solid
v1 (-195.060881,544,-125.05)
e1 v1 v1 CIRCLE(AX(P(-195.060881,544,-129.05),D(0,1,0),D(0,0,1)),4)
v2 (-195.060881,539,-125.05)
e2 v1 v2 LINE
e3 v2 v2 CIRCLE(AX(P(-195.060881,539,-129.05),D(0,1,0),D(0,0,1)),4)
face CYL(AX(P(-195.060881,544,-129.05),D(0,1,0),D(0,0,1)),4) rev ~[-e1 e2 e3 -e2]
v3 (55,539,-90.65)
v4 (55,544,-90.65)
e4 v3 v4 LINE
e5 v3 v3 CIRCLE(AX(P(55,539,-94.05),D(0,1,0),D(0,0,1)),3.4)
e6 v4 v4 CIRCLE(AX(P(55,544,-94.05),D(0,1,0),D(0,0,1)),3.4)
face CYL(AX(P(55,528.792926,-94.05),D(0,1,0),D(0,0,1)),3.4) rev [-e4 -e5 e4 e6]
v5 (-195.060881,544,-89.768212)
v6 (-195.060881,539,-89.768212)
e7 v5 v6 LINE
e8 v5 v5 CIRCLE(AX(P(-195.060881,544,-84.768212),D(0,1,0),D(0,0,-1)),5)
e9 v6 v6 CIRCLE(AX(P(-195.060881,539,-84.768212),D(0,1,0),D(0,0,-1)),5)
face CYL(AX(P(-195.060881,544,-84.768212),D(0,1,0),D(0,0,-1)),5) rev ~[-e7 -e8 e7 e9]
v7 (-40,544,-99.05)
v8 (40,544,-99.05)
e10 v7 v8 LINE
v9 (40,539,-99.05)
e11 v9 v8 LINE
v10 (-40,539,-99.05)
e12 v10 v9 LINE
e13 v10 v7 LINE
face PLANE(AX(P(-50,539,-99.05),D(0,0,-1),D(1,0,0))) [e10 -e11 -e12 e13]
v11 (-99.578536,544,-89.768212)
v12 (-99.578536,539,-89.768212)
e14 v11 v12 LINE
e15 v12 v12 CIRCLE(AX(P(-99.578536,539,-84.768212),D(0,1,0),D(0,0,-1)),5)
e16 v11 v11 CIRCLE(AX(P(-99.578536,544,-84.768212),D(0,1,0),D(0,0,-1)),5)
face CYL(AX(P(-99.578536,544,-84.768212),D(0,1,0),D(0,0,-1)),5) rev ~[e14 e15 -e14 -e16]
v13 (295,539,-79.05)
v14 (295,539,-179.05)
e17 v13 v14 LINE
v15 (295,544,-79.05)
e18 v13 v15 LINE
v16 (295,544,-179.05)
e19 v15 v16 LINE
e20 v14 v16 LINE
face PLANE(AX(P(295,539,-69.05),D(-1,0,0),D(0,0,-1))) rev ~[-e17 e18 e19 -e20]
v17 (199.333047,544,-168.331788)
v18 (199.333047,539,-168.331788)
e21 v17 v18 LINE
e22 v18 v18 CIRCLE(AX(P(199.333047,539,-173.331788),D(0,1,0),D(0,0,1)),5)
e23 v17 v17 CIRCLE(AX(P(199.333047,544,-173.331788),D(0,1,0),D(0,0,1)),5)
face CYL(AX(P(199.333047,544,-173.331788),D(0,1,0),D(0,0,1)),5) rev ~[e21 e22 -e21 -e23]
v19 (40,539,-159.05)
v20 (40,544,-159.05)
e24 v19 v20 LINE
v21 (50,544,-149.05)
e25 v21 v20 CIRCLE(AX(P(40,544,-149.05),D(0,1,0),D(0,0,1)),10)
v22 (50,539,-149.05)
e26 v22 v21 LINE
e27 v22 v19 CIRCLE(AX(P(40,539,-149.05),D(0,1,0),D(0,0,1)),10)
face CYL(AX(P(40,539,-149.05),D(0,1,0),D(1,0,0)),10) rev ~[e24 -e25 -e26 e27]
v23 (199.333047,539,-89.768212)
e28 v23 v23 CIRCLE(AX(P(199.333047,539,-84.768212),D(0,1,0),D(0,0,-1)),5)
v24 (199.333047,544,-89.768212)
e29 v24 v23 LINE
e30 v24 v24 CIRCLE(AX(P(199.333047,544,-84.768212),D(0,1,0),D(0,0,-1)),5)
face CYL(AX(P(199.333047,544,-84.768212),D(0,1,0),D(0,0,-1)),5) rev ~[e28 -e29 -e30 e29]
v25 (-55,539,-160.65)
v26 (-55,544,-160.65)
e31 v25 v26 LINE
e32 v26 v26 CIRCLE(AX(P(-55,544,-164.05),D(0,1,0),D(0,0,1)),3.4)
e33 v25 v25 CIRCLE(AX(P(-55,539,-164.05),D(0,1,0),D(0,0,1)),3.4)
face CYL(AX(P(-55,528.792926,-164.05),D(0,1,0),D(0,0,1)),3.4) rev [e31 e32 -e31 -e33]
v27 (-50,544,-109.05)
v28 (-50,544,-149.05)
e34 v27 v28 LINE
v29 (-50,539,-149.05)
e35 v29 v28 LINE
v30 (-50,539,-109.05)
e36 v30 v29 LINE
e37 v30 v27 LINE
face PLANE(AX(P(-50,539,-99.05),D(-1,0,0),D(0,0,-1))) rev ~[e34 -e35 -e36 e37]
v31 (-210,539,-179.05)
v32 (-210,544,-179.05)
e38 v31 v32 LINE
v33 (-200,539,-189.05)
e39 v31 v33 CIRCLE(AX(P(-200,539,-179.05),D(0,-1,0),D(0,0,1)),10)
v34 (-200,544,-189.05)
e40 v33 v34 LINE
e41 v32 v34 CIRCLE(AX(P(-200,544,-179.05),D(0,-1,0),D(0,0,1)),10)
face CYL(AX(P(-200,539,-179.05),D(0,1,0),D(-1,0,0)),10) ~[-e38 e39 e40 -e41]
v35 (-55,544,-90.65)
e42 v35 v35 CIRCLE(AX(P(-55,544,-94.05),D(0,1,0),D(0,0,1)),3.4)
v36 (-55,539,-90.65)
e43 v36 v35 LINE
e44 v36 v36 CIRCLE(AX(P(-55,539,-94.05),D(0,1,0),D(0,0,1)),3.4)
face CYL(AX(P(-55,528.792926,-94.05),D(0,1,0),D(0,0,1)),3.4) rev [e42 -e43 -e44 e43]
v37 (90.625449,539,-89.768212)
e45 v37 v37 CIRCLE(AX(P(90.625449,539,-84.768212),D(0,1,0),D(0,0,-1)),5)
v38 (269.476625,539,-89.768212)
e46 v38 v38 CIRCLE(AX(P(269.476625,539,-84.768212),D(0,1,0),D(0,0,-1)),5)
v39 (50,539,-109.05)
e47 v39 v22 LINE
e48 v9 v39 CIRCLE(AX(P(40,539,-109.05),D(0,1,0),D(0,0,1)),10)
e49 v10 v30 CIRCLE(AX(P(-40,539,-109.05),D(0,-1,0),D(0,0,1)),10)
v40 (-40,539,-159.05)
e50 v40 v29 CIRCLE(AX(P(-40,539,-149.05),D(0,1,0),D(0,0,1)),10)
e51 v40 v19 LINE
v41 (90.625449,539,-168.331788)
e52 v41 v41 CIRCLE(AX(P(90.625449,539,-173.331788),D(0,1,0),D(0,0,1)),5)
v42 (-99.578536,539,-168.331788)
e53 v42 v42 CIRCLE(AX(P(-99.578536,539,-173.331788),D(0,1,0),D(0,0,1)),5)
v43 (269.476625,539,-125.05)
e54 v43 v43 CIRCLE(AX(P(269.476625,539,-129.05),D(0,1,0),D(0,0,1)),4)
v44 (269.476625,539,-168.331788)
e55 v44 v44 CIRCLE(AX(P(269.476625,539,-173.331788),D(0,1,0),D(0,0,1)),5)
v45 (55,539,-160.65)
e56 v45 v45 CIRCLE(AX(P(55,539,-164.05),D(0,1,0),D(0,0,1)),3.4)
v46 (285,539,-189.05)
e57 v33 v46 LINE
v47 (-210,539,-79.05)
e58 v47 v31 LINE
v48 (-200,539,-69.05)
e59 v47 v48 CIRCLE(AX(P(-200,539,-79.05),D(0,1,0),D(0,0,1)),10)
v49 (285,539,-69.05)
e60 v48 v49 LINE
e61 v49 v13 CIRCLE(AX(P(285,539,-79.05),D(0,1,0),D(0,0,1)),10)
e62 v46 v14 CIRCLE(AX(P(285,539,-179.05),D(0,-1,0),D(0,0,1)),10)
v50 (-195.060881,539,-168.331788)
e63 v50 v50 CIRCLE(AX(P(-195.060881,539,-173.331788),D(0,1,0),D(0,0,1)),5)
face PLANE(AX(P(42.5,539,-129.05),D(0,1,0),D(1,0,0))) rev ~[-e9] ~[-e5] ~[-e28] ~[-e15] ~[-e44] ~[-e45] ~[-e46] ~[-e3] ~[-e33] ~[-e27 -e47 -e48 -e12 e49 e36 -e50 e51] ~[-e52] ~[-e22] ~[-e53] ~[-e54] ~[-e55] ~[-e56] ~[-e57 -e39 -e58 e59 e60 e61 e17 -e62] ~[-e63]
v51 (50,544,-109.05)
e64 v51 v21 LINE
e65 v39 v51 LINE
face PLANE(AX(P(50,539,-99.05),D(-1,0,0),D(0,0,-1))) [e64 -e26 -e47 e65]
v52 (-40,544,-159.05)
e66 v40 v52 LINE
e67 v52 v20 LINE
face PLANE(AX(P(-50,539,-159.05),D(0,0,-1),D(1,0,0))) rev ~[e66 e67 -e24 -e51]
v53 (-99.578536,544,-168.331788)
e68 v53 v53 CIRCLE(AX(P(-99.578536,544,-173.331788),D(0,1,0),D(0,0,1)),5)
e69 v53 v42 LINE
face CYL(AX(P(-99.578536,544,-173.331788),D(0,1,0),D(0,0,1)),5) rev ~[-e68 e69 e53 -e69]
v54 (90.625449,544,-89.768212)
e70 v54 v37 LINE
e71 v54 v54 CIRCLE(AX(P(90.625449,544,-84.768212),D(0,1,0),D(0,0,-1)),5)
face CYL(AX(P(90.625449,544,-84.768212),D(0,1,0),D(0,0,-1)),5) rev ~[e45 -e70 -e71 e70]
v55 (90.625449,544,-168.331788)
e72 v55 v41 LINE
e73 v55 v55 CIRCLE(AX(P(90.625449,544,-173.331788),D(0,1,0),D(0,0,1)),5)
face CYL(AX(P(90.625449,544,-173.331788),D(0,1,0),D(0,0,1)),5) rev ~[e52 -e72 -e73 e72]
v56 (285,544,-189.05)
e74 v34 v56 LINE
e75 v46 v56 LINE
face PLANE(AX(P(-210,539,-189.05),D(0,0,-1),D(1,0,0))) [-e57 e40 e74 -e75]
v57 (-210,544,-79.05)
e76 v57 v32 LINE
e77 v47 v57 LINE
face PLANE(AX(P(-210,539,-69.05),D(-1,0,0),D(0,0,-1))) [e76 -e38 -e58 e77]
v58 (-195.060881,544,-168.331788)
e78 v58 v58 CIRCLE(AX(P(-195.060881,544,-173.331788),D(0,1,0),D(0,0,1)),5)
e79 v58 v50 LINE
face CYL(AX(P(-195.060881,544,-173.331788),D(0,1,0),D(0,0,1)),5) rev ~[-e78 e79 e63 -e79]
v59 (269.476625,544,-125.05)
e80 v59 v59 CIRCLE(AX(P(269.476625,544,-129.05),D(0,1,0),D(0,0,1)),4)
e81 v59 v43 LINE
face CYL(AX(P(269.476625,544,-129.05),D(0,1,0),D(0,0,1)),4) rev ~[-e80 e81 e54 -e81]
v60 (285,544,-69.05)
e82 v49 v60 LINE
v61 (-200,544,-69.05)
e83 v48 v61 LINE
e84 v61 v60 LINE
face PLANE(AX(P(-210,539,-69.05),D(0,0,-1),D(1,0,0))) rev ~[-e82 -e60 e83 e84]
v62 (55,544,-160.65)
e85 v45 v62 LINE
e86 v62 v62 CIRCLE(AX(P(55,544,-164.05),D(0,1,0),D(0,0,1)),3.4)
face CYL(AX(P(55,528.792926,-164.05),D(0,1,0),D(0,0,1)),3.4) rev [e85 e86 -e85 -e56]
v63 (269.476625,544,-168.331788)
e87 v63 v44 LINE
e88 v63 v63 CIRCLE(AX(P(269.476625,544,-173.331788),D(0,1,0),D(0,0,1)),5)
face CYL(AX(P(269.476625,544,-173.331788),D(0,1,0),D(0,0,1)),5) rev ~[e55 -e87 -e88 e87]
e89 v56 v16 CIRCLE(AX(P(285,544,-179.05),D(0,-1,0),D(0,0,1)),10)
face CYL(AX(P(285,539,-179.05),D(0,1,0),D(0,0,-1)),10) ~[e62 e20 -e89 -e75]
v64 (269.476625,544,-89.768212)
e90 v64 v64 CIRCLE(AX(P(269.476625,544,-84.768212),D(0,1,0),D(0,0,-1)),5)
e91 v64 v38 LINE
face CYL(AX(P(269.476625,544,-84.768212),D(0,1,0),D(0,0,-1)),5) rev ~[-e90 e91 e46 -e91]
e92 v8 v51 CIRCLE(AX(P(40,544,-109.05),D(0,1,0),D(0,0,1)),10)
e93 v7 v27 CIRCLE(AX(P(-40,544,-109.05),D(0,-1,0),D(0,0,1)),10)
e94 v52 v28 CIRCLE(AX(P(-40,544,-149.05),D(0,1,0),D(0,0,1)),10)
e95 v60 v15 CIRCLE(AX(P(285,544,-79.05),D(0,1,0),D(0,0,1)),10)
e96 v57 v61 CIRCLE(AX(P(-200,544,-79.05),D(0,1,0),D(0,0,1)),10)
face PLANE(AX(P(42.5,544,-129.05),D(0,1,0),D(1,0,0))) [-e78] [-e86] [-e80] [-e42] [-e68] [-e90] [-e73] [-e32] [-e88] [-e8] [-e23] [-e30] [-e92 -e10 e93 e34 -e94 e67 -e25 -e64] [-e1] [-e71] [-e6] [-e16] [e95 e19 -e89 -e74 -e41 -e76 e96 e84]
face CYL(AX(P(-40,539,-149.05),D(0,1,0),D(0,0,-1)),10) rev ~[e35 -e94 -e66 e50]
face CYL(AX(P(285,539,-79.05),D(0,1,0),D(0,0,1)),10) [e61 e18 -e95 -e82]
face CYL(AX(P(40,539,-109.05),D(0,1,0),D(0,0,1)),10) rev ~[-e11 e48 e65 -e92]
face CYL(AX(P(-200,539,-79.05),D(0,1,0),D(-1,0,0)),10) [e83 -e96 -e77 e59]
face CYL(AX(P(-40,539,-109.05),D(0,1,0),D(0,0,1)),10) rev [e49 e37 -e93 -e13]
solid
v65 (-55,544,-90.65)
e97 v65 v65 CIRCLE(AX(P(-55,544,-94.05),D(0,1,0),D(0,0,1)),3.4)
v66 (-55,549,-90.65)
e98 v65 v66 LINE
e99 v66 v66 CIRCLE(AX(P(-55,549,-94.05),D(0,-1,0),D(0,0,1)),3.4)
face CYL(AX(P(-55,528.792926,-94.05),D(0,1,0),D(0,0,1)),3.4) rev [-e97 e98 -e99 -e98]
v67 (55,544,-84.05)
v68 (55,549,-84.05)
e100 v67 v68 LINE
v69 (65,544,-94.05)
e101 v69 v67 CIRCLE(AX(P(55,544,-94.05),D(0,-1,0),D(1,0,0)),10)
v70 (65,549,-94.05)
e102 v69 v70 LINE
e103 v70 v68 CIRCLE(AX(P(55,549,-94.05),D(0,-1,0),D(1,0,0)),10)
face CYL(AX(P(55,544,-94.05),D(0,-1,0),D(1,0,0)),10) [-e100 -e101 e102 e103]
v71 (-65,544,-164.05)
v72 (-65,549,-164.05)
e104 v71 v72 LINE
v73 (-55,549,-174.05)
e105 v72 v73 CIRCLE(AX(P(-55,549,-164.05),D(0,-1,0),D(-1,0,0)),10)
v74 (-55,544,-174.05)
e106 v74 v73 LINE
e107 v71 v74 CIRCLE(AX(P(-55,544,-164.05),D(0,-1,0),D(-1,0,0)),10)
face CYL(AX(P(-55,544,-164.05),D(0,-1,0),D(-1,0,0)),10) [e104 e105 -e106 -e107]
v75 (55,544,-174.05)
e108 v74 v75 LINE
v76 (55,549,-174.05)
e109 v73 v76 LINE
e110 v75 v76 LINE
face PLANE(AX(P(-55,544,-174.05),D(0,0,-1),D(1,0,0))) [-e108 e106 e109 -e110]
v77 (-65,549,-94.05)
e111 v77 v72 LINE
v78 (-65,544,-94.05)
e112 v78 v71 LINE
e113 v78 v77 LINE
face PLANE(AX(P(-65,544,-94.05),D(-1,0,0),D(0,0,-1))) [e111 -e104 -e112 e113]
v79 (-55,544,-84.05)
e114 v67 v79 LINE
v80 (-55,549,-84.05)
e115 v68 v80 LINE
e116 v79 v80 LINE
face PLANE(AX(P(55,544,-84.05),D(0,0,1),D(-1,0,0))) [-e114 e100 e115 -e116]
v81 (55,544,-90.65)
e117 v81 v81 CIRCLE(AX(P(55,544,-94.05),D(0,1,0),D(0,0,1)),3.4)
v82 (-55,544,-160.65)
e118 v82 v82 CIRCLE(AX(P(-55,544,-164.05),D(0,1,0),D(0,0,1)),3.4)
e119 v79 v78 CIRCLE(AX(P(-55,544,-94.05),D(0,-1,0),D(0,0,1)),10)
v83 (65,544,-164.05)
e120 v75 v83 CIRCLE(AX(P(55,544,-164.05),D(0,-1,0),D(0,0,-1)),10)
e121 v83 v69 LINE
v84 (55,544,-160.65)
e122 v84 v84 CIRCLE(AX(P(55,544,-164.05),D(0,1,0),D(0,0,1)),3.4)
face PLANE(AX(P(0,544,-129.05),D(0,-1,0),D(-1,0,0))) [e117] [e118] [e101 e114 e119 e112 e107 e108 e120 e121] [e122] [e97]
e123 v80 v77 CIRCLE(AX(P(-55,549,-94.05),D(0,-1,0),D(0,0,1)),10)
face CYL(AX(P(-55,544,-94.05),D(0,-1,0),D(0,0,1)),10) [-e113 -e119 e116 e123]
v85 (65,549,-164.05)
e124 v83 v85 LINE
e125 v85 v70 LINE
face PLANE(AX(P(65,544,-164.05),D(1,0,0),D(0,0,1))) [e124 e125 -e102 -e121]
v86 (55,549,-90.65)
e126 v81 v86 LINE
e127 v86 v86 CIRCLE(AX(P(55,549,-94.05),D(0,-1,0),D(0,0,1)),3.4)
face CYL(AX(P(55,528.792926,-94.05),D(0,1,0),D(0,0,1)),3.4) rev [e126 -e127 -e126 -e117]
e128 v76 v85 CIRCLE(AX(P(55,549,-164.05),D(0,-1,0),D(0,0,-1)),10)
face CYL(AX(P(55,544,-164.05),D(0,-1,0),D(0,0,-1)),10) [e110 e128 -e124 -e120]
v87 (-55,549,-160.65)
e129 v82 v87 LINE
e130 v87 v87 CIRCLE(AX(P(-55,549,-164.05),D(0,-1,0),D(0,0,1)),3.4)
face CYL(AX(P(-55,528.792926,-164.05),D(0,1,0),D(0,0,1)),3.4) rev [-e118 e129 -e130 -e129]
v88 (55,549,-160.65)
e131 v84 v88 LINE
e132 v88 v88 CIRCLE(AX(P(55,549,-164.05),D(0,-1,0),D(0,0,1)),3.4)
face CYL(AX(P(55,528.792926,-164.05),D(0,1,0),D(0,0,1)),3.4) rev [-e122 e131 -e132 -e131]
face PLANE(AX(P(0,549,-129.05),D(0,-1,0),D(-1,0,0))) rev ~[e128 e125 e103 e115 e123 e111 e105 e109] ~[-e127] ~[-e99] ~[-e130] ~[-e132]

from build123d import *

# Parameters (mm, degrees)
SKETCH1_W                  = 505
SKETCH1_H                  = 120
SKETCH1_W_2                = 100
SKETCH1_H_2                = 60
BOSS_EXTRUDE1_DEPTH        = 5
FILLET1_R                  = 10
FILLET2_R                  = 10
BOSS_EXTRUDE2_DEPTH        = 5
M8_TAPPED_HOLE1_AT_2_COUNT = 2
M8_TAPPED_HOLE1_AT_2_PITCH = 110
M8_TAPPED_HOLE1_AT_3_COUNT = 2
M8_TAPPED_HOLE1_AT_3_PITCH = 70
M8_TAPPED_HOLE1_AT_4_COUNT = 2
M8_TAPPED_HOLE1_AT_4_PITCH = 130.384048104
SKETCH5_R                  = 5
SKETCH5_R_2                = 4
CUT_EXTRUDE1_DEPTH         = 20


with BuildPart() as part:
    # Sketch1 → Boss-Extrude1 (new body)
    with BuildSketch(Plane(origin=(0, 539, 0), x_dir=(1, 0, 0), z_dir=(0, 1, 0))):
        with Locations((42.5, 129.05)):
            Rectangle(SKETCH1_W, SKETCH1_H)
        with Locations((0, 129.05)):
            Rectangle(SKETCH1_W_2, SKETCH1_H_2, mode=Mode.SUBTRACT)
    extrude(amount=BOSS_EXTRUDE1_DEPTH)

    # Fillet1
    fillet1_edges = [part.edges().sort_by_distance(p)[0] for p in [
        (-210, 541.5, -189.05),
        (295, 541.5, -189.05),
        (295, 541.5, -69.05),
        (-210, 541.5, -69.05),
    ]]
    fillet(fillet1_edges, radius=FILLET1_R)

    # Fillet2
    fillet2_edges = [part.edges().sort_by_distance(p)[0] for p in [
        (-50, 541.5, -159.05),
        (-50, 541.5, -99.05),
        (50, 541.5, -99.05),
        (50, 541.5, -159.05),
    ]]
    fillet(fillet2_edges, radius=FILLET2_R)


with BuildPart() as body_2:
    # Sketch2 → Boss-Extrude2 (new body)
    with BuildSketch(Plane(origin=(0, 544, 0), x_dir=(1, 0, 0), z_dir=(0, 1, 0))):
        with BuildLine():
            Line((-55, 174.05), (55, 174.05))
            ThreePointArc((55, 174.05), (62.071067812, 171.121067812), (65, 164.05))
            Line((65, 164.05), (65, 94.05))
            ThreePointArc((65, 94.05), (62.071067812, 86.978932188), (55, 84.05))
            Line((55, 84.05), (-55, 84.05))
            ThreePointArc((-55, 84.05), (-62.071067812, 86.978932188), (-65, 94.05))
            Line((-65, 94.05), (-65, 164.05))
            ThreePointArc((-65, 164.05), (-62.071067812, 171.121067812), (-55, 174.05))
        make_face()
    extrude(amount=BOSS_EXTRUDE2_DEPTH)


with BuildPart() as m8_tapped_hole1_tool:
    # Sketch4 → M8 Tapped Hole1 (revolve)
    with BuildSketch(Plane(origin=(-55, 549, -164.05), x_dir=(0, 0, 1), z_dir=(1, 0, 0))):
        Polygon((0, 0), (0, 22.25), (3.4, 20.207073895), (3.4, 0), align=None)
    m8_tapped_hole1 = revolve(axis=Axis((-55, 555.35, -164.05), (0, -1, 0)))


with BuildPart() as part_1:
    add(part.part)

    # M8 Tapped Hole1: cut by m8_tapped_hole1_tool
    add(m8_tapped_hole1_tool.part, mode=Mode.SUBTRACT)


with BuildPart() as body_2_1:
    add(body_2.part)

    # M8 Tapped Hole1: cut by m8_tapped_hole1_tool
    add(m8_tapped_hole1_tool.part, mode=Mode.SUBTRACT)


with BuildPart() as m8_tapped_hole1_at_2_tool:
    # M8 Tapped Hole1 at 2: M8 Tapped Hole1 ×2
    with Locations(*[(i * M8_TAPPED_HOLE1_AT_2_PITCH, 0, 0) for i in range(1, M8_TAPPED_HOLE1_AT_2_COUNT)]):
        add(m8_tapped_hole1)


with BuildPart() as part_2:
    add(part_1.part)

    # M8 Tapped Hole1 at 2: cut by m8_tapped_hole1_at_2_tool
    add(m8_tapped_hole1_at_2_tool.part, mode=Mode.SUBTRACT)


with BuildPart() as body_2_2:
    add(body_2_1.part)

    # M8 Tapped Hole1 at 2: cut by m8_tapped_hole1_at_2_tool
    add(m8_tapped_hole1_at_2_tool.part, mode=Mode.SUBTRACT)


with BuildPart() as m8_tapped_hole1_at_3_tool:
    # M8 Tapped Hole1 at 3: M8 Tapped Hole1 ×2
    with Locations(*[(0, 0, i * M8_TAPPED_HOLE1_AT_3_PITCH) for i in range(1, M8_TAPPED_HOLE1_AT_3_COUNT)]):
        add(m8_tapped_hole1)


with BuildPart() as part_3:
    add(part_2.part)

    # M8 Tapped Hole1 at 3: cut by m8_tapped_hole1_at_3_tool
    add(m8_tapped_hole1_at_3_tool.part, mode=Mode.SUBTRACT)


with BuildPart() as body_2_3:
    add(body_2_2.part)

    # M8 Tapped Hole1 at 3: cut by m8_tapped_hole1_at_3_tool
    add(m8_tapped_hole1_at_3_tool.part, mode=Mode.SUBTRACT)


with BuildPart() as m8_tapped_hole1_at_4_tool:
    # M8 Tapped Hole1 at 4: M8 Tapped Hole1 ×2
    with Locations(*[Vector(0.8436614877321076, 0, 0.5368754921931594) * (i * M8_TAPPED_HOLE1_AT_4_PITCH) for i in range(1, M8_TAPPED_HOLE1_AT_4_COUNT)]):
        add(m8_tapped_hole1)


with BuildPart() as part_4:
    add(part_3.part)

    # M8 Tapped Hole1 at 4: cut by m8_tapped_hole1_at_4_tool
    add(m8_tapped_hole1_at_4_tool.part, mode=Mode.SUBTRACT)

    # Sketch5 → Cut-Extrude1 (cut)
    with BuildSketch(Plane(origin=(0, 544, 0), x_dir=(1, 0, 0), z_dir=(0, 1, 0))):
        with Locations(Location((-195.060881063, 173.331788152, 0), (0, 0, 270))):
            Circle(SKETCH5_R)
        with Locations(Location((-99.578535876, 173.331788152, 0), (0, 0, 270))):
            Circle(SKETCH5_R)
        with Locations(Location((90.625449249, 173.331788152, 0), (0, 0, 270))):
            Circle(SKETCH5_R)
        with Locations(Location((199.333046544, 173.331788152, 0), (0, 0, 270))):
            Circle(SKETCH5_R)
        with Locations(Location((269.476624658, 173.331788152, 0), (0, 0, 270))):
            Circle(SKETCH5_R)
        with Locations(Location((269.476624658, 129.05, 0), (0, 0, 270))):
            Circle(SKETCH5_R_2)
        with Locations(Location((-195.060881063, 129.05, 0), (0, 0, 270))):
            Circle(SKETCH5_R_2)
        with Locations(Location((269.476624658, 84.768211848, 0), (0, 0, 90))):
            Circle(SKETCH5_R)
        with Locations(Location((199.333046544, 84.768211848, 0), (0, 0, 90))):
            Circle(SKETCH5_R)
        with Locations(Location((90.625449249, 84.768211848, 0), (0, 0, 90))):
            Circle(SKETCH5_R)
        with Locations(Location((-99.578535876, 84.768211848, 0), (0, 0, 90))):
            Circle(SKETCH5_R)
        with Locations(Location((-195.060881063, 84.768211848, 0), (0, 0, 90))):
            Circle(SKETCH5_R)
    extrude(amount=-CUT_EXTRUDE1_DEPTH, mode=Mode.SUBTRACT)


with BuildPart() as body_2_4:
    add(body_2_3.part)

    # M8 Tapped Hole1 at 4: cut by m8_tapped_hole1_at_4_tool
    add(m8_tapped_hole1_at_4_tool.part, mode=Mode.SUBTRACT)


solid = Compound([part_4.part, body_2_4.part])
